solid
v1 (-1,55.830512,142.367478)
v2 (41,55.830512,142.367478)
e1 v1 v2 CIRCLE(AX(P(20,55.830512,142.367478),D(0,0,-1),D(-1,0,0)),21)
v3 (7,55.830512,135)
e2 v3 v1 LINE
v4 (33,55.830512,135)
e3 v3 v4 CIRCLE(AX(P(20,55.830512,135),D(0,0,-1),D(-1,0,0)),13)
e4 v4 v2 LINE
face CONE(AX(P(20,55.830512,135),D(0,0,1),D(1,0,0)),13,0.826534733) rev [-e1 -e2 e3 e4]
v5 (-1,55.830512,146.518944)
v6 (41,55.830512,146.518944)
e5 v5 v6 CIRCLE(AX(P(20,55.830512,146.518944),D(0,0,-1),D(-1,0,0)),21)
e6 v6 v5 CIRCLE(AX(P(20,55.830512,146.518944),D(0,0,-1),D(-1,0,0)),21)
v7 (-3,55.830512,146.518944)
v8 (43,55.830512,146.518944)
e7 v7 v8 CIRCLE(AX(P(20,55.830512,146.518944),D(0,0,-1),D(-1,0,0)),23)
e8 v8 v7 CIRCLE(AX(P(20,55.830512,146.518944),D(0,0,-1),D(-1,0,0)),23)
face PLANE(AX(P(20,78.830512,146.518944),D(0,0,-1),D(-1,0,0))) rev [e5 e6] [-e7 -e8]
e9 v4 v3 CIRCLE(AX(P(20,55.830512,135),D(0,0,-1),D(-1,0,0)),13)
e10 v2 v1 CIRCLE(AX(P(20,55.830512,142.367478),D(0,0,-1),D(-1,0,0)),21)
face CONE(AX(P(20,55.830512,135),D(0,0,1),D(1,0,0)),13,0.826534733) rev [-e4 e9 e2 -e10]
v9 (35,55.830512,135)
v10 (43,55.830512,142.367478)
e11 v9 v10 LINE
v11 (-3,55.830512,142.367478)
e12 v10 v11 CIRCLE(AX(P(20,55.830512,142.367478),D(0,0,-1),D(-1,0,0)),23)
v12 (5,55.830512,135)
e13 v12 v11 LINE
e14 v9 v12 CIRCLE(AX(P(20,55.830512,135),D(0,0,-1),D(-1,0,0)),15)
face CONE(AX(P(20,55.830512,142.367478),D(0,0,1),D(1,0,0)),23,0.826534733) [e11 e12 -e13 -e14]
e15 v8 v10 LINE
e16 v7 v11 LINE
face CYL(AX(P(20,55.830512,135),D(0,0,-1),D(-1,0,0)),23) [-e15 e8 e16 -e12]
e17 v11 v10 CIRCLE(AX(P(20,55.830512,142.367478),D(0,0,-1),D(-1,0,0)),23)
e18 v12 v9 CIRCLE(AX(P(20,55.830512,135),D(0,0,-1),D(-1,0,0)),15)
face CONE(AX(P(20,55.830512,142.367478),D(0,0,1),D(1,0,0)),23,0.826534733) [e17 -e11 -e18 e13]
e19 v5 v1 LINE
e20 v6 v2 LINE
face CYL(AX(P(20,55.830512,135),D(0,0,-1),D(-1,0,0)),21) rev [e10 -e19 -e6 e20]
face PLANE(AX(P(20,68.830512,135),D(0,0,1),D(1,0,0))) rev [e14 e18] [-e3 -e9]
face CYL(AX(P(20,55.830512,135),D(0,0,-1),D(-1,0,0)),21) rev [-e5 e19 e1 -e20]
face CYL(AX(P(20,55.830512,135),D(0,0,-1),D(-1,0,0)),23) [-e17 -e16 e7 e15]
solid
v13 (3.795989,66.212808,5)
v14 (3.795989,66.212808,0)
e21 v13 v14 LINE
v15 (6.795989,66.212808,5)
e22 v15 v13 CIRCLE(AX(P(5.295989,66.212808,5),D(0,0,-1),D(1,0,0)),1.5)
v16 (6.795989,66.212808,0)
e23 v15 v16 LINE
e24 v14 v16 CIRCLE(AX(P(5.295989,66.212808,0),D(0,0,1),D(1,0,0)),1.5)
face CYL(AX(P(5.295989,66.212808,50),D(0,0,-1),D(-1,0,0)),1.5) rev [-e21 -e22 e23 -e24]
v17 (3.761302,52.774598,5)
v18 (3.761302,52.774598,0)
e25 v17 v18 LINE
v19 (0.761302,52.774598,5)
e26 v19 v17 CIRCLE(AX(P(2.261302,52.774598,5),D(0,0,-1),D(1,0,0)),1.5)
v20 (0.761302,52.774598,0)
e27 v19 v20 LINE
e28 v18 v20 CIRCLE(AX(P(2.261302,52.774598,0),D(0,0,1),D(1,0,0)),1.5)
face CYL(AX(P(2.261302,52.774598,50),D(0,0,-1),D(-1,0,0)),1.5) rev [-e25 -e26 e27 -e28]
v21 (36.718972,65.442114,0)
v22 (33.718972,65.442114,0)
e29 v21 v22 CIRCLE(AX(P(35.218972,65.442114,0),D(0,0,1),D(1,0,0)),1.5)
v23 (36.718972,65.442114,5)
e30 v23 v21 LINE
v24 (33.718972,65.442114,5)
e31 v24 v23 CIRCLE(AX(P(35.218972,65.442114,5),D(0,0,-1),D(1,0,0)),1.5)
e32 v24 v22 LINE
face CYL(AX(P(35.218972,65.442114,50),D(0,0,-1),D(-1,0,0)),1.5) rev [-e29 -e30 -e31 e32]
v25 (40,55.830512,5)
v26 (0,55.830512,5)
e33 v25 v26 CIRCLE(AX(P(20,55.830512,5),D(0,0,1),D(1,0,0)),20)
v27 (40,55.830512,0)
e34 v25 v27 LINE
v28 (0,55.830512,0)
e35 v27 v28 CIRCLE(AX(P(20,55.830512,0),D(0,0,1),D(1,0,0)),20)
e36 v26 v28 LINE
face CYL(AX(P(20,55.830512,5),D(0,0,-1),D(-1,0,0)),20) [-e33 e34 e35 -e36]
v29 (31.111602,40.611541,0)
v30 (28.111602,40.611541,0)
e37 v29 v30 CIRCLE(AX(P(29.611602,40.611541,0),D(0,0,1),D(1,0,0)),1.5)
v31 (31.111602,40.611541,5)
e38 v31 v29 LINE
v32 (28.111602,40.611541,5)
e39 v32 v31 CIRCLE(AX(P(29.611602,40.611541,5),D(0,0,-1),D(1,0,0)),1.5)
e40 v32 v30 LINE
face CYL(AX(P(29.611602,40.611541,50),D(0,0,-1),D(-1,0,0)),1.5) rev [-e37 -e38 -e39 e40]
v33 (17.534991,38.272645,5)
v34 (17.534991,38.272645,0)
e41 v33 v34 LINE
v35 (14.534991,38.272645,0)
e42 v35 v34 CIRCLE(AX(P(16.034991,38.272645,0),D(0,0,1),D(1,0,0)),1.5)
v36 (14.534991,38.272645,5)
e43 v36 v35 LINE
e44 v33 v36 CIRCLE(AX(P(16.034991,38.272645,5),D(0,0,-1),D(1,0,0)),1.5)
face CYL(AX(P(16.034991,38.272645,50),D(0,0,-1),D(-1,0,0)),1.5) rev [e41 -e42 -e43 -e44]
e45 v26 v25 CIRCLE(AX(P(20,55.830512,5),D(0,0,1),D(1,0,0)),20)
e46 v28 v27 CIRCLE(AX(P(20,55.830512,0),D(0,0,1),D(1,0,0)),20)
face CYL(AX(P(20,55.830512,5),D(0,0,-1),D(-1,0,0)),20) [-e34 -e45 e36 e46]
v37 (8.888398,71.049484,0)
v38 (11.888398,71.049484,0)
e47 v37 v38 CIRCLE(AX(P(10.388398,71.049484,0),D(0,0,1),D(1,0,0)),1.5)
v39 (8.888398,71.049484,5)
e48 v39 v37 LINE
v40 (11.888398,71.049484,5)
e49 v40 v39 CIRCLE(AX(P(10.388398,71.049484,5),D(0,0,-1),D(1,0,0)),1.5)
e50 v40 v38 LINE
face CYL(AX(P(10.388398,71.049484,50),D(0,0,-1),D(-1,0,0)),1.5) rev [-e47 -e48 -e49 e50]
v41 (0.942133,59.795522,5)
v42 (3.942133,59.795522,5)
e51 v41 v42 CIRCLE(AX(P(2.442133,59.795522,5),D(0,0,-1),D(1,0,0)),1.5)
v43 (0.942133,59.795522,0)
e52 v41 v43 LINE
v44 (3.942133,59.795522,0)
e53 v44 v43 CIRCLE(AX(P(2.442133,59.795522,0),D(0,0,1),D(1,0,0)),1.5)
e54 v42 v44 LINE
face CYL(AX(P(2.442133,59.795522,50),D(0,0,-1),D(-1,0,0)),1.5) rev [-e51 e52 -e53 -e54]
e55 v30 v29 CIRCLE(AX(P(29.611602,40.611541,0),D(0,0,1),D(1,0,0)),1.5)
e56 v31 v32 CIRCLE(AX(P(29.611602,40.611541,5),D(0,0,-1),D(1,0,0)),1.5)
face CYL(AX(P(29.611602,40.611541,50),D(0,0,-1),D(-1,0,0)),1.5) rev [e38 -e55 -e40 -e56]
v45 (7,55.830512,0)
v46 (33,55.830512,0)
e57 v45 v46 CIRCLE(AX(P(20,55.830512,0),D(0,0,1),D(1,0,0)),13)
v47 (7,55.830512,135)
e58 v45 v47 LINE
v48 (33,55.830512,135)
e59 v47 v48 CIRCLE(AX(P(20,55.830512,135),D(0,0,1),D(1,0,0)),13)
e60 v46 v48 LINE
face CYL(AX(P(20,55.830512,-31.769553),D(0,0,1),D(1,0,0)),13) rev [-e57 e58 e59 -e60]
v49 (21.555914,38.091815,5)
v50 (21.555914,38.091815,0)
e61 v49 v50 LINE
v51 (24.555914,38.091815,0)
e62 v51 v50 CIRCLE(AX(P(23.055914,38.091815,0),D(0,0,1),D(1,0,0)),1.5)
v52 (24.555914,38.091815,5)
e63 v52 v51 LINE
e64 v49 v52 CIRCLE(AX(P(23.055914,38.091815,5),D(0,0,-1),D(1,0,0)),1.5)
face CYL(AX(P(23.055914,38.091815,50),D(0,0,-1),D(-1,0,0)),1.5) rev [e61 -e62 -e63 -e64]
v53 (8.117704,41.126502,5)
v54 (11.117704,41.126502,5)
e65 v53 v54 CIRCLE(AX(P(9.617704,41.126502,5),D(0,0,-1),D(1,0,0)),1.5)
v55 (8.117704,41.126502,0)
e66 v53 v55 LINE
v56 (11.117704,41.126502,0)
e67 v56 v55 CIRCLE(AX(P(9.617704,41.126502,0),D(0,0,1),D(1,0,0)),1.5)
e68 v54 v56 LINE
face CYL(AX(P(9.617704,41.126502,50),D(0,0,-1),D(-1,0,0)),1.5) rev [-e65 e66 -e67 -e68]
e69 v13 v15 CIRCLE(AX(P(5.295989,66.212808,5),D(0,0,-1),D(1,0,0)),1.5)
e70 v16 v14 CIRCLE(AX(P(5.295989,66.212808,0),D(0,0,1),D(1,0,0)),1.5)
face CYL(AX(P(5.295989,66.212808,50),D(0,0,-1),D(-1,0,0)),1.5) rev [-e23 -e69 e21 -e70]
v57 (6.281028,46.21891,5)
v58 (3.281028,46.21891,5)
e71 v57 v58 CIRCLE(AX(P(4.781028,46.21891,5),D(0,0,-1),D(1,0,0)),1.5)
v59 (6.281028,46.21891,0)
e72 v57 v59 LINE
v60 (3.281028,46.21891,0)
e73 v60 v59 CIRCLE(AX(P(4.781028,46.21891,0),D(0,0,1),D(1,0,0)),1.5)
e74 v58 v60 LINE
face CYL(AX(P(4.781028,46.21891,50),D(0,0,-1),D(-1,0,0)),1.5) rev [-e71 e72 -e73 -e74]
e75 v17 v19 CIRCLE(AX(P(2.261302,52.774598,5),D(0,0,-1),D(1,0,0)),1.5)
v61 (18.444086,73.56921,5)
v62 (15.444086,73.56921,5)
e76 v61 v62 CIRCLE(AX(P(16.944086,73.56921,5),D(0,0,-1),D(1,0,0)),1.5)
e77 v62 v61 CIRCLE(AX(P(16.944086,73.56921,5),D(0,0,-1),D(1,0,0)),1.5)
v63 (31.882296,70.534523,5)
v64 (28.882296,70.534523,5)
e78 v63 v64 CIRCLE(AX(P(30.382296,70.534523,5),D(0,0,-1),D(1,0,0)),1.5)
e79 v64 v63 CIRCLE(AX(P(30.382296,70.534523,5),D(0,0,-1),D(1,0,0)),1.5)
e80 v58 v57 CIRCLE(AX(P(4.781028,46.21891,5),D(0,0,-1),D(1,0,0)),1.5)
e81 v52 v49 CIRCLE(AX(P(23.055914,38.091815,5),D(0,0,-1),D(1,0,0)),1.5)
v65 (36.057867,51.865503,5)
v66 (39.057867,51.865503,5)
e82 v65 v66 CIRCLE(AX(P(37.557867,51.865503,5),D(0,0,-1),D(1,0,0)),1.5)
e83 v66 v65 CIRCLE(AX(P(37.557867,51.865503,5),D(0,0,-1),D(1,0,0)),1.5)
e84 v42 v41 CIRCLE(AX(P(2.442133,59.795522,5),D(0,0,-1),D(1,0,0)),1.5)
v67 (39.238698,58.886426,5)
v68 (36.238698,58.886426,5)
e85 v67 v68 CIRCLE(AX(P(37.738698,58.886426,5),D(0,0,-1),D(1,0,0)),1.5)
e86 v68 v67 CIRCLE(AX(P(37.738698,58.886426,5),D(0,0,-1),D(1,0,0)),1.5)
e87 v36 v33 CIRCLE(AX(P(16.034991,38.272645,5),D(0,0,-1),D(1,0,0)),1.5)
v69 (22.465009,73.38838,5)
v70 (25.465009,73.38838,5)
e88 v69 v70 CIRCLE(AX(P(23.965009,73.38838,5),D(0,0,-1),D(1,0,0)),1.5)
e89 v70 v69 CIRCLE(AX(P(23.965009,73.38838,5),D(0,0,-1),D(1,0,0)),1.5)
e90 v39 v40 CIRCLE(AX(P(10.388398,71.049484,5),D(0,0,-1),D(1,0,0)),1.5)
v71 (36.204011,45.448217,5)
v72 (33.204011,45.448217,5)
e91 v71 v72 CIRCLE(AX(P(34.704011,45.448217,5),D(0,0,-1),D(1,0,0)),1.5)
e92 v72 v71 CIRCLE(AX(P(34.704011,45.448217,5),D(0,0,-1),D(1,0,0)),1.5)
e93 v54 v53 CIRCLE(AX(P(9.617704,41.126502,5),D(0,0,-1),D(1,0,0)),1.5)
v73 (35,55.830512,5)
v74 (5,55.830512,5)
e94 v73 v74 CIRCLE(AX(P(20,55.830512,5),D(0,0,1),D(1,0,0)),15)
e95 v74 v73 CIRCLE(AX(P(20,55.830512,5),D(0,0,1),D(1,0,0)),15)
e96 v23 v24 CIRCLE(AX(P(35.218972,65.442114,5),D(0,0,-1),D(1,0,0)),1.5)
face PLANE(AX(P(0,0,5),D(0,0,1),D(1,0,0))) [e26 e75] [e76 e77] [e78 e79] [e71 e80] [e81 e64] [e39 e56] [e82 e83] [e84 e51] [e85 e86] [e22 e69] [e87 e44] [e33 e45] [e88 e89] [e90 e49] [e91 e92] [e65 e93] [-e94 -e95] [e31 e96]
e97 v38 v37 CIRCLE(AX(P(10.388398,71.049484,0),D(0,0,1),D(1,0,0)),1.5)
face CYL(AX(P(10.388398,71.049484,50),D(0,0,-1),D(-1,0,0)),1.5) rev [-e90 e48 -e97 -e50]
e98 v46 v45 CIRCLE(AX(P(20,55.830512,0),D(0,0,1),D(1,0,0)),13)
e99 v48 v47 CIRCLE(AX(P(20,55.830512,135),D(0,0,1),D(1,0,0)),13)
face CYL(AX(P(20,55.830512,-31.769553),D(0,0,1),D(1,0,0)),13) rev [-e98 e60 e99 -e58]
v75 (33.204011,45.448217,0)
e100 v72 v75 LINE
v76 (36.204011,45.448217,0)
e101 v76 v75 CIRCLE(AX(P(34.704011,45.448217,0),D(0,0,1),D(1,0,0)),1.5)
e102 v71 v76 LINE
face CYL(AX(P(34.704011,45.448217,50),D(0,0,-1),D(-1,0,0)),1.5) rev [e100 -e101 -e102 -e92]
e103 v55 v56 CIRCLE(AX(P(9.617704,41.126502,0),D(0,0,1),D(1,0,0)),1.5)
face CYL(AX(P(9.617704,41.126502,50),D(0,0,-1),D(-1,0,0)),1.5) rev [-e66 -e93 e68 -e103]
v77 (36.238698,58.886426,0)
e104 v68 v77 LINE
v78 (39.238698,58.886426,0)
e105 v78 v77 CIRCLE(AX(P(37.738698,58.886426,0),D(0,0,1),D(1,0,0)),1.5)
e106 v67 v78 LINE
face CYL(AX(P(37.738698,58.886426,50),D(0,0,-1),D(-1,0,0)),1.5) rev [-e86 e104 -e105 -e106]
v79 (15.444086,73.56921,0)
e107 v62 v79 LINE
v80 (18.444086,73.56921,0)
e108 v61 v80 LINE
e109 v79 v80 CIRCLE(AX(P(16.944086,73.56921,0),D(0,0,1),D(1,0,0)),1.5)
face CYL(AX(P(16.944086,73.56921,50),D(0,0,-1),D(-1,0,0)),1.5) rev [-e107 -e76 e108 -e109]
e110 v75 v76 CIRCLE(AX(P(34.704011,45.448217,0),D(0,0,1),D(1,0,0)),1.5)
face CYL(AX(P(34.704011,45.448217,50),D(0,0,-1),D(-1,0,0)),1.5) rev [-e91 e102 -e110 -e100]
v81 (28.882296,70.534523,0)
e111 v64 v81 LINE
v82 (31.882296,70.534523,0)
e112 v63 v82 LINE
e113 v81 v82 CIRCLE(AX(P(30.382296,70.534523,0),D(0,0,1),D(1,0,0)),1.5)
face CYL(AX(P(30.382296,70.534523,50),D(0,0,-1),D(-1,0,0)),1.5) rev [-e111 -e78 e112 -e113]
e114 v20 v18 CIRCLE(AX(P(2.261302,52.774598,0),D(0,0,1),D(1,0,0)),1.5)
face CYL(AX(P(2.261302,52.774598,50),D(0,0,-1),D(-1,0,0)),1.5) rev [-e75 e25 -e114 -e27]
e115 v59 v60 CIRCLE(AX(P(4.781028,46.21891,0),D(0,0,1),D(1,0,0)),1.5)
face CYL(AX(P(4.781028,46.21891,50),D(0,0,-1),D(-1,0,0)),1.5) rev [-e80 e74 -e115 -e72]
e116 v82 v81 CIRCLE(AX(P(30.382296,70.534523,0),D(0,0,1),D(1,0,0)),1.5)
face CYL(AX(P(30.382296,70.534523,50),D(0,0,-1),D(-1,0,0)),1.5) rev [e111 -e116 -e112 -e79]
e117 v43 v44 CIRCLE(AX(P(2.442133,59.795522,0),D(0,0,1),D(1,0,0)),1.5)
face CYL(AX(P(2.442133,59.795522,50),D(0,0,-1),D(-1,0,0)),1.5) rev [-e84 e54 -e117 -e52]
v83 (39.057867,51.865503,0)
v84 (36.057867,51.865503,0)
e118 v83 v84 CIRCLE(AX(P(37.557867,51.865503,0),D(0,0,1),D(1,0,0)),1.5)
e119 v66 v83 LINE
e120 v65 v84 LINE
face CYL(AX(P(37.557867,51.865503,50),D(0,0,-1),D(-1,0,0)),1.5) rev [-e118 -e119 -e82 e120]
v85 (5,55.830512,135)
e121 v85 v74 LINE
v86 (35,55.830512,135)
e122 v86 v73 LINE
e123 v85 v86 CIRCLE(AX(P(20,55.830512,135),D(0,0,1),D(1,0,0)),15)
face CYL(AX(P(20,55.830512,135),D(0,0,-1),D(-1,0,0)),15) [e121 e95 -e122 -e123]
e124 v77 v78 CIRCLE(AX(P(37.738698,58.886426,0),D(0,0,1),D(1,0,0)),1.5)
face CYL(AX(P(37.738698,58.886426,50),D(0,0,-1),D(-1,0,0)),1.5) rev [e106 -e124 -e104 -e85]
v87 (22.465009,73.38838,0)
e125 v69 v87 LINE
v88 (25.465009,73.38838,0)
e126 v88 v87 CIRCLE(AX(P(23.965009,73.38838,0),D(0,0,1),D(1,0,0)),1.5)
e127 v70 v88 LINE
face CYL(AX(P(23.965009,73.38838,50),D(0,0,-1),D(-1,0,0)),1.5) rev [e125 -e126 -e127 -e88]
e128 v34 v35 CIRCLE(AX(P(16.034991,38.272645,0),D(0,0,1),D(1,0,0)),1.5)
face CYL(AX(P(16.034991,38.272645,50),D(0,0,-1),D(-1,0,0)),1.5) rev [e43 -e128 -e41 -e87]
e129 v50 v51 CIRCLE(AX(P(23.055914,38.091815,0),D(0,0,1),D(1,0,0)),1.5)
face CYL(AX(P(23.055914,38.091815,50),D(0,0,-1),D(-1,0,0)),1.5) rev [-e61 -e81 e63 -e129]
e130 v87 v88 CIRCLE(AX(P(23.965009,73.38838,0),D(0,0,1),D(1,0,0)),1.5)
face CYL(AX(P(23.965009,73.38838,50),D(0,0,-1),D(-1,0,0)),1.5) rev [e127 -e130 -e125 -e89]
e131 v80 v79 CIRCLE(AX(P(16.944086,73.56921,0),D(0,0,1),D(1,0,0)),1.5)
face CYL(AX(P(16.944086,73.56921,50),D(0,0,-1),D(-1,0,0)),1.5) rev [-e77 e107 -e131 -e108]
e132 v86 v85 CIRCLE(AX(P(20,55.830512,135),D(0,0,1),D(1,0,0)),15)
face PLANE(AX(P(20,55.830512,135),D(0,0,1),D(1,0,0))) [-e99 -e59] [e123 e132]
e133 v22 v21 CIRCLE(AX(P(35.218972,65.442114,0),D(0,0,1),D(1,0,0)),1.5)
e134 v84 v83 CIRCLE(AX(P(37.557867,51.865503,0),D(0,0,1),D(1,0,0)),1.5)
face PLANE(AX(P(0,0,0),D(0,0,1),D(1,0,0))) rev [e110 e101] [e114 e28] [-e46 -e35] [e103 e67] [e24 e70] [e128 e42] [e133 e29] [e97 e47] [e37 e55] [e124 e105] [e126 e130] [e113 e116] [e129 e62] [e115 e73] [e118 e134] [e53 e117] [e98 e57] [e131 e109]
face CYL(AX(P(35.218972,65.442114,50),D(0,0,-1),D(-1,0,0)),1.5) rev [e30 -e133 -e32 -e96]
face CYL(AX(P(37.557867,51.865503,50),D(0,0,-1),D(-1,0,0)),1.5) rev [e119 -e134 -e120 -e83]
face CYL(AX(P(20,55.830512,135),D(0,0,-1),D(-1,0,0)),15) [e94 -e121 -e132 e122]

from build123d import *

# Parameters (mm, degrees)
SKETCH1_R               = 20
SKETCH1_R_2             = 15
BOSS_EXTRUDE1_DEPTH     = 5
SKETCH2_R               = 15
BOSS_EXTRUDE2_DEPTH     = 130
CUT_EXTRUDE1_DEPTH      = 160.922689506
CUT_EXTRUDE1_DEPTH_BACK = 130
SKETCH3_R               = 13
SKETCH4_R               = 13
CUT_EXTRUDE2_DEPTH      = 156.724971083
SKETCH11_R              = 1.5
CUT_EXTRUDE4_DEPTH      = 50


with BuildPart() as part:
    # Sketch1 → Boss-Extrude1 (new body)
    # profile 1 of 2: a face of its own
    with BuildSketch(Plane.XY):
        with Locations((20, 55.830512452)):
            Circle(SKETCH1_R)
        with Locations((20, 55.830512452)):
            Circle(SKETCH1_R_2, mode=Mode.SUBTRACT)
    # profile 2 of 2: a face of its own
    with BuildSketch(Plane.XY):
        with Locations((20, 55.830512452)):
            Circle(SKETCH1_R_2)
    extrude(amount=BOSS_EXTRUDE1_DEPTH)

    # Sketch2 → Boss-Extrude2 (add)
    with BuildSketch(Plane.XY.offset(5)):
        with Locations((20, 55.830512452)):
            Circle(SKETCH2_R)
    extrude(amount=BOSS_EXTRUDE2_DEPTH)

    # Sketch3 → Cut-Extrude1 (cut, two sides: drawn at the far end of the back side and taken through both)
    with BuildSketch(Plane.XY.offset(135).offset(-CUT_EXTRUDE1_DEPTH_BACK)):
        with Locations((20, 55.830512452)):
            Circle(SKETCH3_R)
    extrude(amount=CUT_EXTRUDE1_DEPTH + CUT_EXTRUDE1_DEPTH_BACK, mode=Mode.SUBTRACT)

    # Sketch4 → Cut-Extrude2 (cut, through all)
    with BuildSketch(Plane.XY.offset(5)):
        with Locations((20, 55.830512452)):
            Circle(SKETCH4_R)
    extrude(amount=-CUT_EXTRUDE2_DEPTH, mode=Mode.SUBTRACT)

    # Sketch11 → Cut-Extrude4 (cut)
    with BuildSketch(Plane.XY):
        with Locations((10.388397973, 71.049484377)):
            Circle(SKETCH11_R)
        with Locations((16.944086026, 73.569209974)):
            Circle(SKETCH11_R)
        with Locations((23.96500928, 73.388379674)):
            Circle(SKETCH11_R)
        with Locations((30.382295814, 70.534523253)):
            Circle(SKETCH11_R)
        with Locations((35.218971926, 65.442114479)):
            Circle(SKETCH11_R)
        with Locations((37.738697522, 58.886426426)):
            Circle(SKETCH11_R)
        with Locations((37.557867223, 51.865503172)):
            Circle(SKETCH11_R)
        with Locations((34.704010801, 45.448216638)):
            Circle(SKETCH11_R)
        with Locations((29.611602027, 40.611540526)):
            Circle(SKETCH11_R)
        with Locations((23.055913974, 38.09181493)):
            Circle(SKETCH11_R)
        with Locations((16.03499072, 38.272645229)):
            Circle(SKETCH11_R)
        with Locations((9.617704186, 41.126501651)):
            Circle(SKETCH11_R)
        with Locations((4.781028074, 46.218910425)):
            Circle(SKETCH11_R)
        with Locations((2.261302478, 52.774598478)):
            Circle(SKETCH11_R)
        with Locations((2.442132777, 59.795521732)):
            Circle(SKETCH11_R)
        with Locations((5.295989199, 66.212808266)):
            Circle(SKETCH11_R)
    extrude(amount=CUT_EXTRUDE4_DEPTH, mode=Mode.SUBTRACT)


with BuildPart() as body_2:
    # Sketch7 → Revolve1 (revolve)
    with BuildSketch(Plane.ZY.offset(-20), mode=Mode.PRIVATE) as revolve1_sk:
        Polygon((135, 68.830512452), (135, 70.830512452), (142.367477853, 78.830512452), (146.518943946, 78.830512452), (146.518943946, 76.830512452), (142.367477853, 76.830512452), align=None)
    revolve(revolve1_sk.sketch.rotate(Axis((20, 55.830512452, 135), (0, 0, 1)), 90), axis=Axis((20, 55.830512452, 135), (0, 0, 1)))


solid = Compound([part.part, body_2.part])
